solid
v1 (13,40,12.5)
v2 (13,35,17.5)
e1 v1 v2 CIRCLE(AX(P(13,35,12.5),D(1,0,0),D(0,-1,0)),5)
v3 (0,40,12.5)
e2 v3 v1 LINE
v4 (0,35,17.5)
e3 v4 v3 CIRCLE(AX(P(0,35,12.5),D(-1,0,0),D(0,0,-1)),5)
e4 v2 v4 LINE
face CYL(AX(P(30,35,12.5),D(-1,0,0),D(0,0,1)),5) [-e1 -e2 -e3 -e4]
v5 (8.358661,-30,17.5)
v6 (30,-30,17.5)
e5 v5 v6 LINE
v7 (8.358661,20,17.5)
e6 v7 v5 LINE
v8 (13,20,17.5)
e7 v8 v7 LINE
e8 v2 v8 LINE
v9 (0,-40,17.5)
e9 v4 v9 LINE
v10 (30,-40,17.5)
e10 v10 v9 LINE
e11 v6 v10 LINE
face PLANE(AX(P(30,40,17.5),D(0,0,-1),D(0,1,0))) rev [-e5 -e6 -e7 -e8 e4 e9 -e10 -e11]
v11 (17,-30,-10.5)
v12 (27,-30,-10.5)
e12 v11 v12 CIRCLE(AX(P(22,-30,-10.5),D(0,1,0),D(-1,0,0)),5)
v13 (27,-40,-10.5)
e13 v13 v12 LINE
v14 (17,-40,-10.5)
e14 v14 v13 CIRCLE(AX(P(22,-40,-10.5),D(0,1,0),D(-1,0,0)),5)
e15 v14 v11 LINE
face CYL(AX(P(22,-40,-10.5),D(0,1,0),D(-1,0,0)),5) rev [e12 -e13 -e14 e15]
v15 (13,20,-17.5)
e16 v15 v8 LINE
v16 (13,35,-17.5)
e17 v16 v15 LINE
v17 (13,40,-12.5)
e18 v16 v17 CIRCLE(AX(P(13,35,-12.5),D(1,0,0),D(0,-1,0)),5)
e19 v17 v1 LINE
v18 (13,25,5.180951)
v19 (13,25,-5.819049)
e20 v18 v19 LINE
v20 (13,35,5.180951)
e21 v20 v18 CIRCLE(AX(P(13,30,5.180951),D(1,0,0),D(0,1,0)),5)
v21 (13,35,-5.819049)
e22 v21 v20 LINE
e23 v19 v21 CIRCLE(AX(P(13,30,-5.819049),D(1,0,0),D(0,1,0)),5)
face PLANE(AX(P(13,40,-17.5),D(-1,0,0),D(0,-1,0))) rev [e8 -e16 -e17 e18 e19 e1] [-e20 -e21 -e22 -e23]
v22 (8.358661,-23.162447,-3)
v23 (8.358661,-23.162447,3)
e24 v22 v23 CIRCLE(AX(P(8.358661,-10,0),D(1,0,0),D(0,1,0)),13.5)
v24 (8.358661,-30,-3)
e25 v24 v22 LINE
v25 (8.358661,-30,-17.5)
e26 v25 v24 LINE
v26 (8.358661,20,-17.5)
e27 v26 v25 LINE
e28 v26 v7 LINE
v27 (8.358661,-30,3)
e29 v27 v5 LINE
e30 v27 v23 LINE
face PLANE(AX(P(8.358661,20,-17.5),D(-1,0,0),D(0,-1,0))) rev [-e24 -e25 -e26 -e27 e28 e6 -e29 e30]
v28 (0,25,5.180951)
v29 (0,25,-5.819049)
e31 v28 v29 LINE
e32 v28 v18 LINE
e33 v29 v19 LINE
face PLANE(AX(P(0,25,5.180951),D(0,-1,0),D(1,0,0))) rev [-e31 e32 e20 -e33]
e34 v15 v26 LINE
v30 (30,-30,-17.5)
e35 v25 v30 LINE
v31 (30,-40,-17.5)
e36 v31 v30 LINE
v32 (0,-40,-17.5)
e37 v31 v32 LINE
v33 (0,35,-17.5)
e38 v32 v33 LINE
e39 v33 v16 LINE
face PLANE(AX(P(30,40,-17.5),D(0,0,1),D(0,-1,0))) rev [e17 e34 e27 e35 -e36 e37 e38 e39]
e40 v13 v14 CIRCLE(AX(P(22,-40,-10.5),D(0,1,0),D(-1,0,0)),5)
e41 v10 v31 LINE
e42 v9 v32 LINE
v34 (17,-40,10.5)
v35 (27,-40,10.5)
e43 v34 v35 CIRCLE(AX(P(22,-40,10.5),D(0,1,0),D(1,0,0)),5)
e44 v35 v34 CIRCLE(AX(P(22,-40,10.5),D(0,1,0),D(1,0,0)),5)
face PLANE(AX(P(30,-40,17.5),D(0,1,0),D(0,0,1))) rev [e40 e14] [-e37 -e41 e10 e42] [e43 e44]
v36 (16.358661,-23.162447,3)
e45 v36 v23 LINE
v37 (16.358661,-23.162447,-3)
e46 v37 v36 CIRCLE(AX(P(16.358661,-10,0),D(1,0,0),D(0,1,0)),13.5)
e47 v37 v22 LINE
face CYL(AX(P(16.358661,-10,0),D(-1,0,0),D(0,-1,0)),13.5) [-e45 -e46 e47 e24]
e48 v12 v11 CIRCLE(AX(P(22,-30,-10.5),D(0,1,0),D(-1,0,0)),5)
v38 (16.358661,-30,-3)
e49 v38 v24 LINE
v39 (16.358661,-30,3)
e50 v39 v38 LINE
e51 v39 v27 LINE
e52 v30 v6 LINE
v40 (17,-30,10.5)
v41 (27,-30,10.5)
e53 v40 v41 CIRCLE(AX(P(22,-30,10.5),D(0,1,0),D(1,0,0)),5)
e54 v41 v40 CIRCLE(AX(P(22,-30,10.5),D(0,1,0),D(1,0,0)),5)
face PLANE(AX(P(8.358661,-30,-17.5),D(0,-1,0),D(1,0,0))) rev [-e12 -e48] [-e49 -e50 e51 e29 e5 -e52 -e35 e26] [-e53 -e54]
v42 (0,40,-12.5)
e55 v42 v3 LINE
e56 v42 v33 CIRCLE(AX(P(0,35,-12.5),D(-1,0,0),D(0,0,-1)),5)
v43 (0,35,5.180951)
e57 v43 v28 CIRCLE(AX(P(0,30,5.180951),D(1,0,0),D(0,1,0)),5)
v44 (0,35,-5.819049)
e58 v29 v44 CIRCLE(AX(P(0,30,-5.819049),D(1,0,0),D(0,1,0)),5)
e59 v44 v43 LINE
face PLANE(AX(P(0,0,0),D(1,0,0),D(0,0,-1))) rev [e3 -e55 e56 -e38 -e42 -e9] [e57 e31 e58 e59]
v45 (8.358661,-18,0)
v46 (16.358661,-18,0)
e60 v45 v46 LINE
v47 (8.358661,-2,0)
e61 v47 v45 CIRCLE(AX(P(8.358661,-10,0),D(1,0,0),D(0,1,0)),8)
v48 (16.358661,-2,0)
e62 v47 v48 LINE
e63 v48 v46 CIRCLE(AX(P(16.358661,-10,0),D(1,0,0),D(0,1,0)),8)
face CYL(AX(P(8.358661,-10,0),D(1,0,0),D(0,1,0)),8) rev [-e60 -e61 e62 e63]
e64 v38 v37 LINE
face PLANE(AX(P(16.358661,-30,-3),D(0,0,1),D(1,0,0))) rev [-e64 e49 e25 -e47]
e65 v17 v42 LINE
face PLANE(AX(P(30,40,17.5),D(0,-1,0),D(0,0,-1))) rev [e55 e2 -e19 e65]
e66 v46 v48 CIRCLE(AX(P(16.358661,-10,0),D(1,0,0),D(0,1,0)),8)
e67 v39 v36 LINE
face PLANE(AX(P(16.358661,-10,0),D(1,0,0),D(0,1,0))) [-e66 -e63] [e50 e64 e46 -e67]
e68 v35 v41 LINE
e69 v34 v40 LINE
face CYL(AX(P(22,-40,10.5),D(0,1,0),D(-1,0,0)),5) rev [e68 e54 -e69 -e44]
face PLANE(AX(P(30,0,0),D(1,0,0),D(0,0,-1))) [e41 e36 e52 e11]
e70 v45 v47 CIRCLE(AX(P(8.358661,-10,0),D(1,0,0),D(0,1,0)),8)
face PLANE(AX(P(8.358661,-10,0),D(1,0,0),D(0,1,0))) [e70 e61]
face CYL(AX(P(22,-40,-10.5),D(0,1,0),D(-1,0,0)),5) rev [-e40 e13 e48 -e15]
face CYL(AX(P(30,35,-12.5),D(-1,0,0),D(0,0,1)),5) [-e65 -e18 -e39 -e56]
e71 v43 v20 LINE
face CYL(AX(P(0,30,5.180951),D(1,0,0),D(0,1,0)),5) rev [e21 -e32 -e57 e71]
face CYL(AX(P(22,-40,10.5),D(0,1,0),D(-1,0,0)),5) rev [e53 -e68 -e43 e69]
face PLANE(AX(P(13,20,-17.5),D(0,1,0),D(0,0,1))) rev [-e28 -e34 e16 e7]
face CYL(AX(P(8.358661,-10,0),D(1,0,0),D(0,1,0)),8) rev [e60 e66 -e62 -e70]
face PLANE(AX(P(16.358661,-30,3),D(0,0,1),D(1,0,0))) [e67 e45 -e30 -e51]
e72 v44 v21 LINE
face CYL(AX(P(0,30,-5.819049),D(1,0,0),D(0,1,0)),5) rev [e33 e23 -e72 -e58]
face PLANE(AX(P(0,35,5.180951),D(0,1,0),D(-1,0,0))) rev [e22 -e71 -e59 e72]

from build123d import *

# Parameters (mm, degrees)
BRACKET_PROFILE_SKETCH_W = 35
BRACKET_PROFILE_SKETCH_H = 80
BRACKET_BODY_DEPTH       = 30
SIDE_RELIEF_CUT_DEPTH    = 62.032778079
RING_BOSS_DEPTH          = 8
BOSS_BORE_SKETCH_R       = 8
BOSS_BORE_16_DEPTH       = 8
BASE_HOLES_SKETCH_R      = 5
BASE_HOLES_DEPTH         = 79.14249804
EDGE_FILLET_R5_R         = 5
TOP_SLOT_CUT_DEPTH       = 47.853495067


with BuildPart() as part:
    # Bracket Profile Sketch → Bracket Body (new body)
    with BuildSketch(Plane(origin=(0, 0, 0), x_dir=(0, 0, -1), z_dir=(1, 0, 0))):
        Rectangle(BRACKET_PROFILE_SKETCH_W, BRACKET_PROFILE_SKETCH_H)
    extrude(amount=BRACKET_BODY_DEPTH)

    # Side Relief Sketch → Side Relief Cut (cut, through all)
    with BuildSketch(Plane.XY.offset(17.5)):
        Polygon((13, 40), (13, 20), (8.358661264, 20), (8.358661264, -30), (30, -30), (30, 40), align=None)
    extrude(amount=-SIDE_RELIEF_CUT_DEPTH, mode=Mode.SUBTRACT)

    # Ring Boss Sketch → Ring Boss (add)
    with BuildSketch(Plane(origin=(8.358661264, 0, 0), x_dir=(0, 0, -1), z_dir=(1, 0, 0))):
        with BuildLine():
            Line((-3, -30), (3, -30))
            Line((3, -30), (3, -23.162446581))
            ThreePointArc((3, -23.162446581), (0, 3.5), (-3, -23.162446581))
            Line((-3, -23.162446581), (-3, -30))
        make_face()
    extrude(amount=RING_BOSS_DEPTH)

    # Boss Bore Sketch → Boss Bore Ø16 (cut)
    with BuildSketch(Plane(origin=(16.358661264, 0, 0), x_dir=(0, 0, -1), z_dir=(1, 0, 0))):
        with Locations(Location((0, -10, 0), (0, 0, 90))):
            Circle(BOSS_BORE_SKETCH_R)
    extrude(amount=-BOSS_BORE_16_DEPTH, mode=Mode.SUBTRACT)

    # Base Holes Sketch → Base Holes (cut, through all)
    with BuildSketch(Plane(origin=(0, -30, 0), x_dir=(1, 0, 0), z_dir=(0, 1, 0))):
        with Locations(Location((22, 10.5, 0), (0, 0, 180))):
            Circle(BASE_HOLES_SKETCH_R)
        with Locations((22, -10.5)):
            Circle(BASE_HOLES_SKETCH_R)
    extrude(amount=-BASE_HOLES_DEPTH, mode=Mode.SUBTRACT)

    # Edge Fillet R5
    edge_fillet_r5_edges = [part.edges().sort_by_distance(p)[0] for p in [
        (6.5, 40, 17.5),
        (6.5, 40, -17.5),
    ]]
    fillet(edge_fillet_r5_edges, radius=EDGE_FILLET_R5_R)

    # Top Slot Sketch → Top Slot Cut (cut, through all)
    with BuildSketch(Plane(origin=(13, 0, 0), x_dir=(0, 0, -1), z_dir=(1, 0, 0))):
        with BuildLine():
            Line((-5.180950854, 35), (5.819049146, 35))
            ThreePointArc((5.819049146, 35), (10.819049146, 30), (5.819049146, 25))
            Line((5.819049146, 25), (-5.180950854, 25))
            ThreePointArc((-5.180950854, 25), (-10.180950854, 30), (-5.180950854, 35))
        make_face()
    extrude(amount=-TOP_SLOT_CUT_DEPTH, mode=Mode.SUBTRACT)


solid = part.part
